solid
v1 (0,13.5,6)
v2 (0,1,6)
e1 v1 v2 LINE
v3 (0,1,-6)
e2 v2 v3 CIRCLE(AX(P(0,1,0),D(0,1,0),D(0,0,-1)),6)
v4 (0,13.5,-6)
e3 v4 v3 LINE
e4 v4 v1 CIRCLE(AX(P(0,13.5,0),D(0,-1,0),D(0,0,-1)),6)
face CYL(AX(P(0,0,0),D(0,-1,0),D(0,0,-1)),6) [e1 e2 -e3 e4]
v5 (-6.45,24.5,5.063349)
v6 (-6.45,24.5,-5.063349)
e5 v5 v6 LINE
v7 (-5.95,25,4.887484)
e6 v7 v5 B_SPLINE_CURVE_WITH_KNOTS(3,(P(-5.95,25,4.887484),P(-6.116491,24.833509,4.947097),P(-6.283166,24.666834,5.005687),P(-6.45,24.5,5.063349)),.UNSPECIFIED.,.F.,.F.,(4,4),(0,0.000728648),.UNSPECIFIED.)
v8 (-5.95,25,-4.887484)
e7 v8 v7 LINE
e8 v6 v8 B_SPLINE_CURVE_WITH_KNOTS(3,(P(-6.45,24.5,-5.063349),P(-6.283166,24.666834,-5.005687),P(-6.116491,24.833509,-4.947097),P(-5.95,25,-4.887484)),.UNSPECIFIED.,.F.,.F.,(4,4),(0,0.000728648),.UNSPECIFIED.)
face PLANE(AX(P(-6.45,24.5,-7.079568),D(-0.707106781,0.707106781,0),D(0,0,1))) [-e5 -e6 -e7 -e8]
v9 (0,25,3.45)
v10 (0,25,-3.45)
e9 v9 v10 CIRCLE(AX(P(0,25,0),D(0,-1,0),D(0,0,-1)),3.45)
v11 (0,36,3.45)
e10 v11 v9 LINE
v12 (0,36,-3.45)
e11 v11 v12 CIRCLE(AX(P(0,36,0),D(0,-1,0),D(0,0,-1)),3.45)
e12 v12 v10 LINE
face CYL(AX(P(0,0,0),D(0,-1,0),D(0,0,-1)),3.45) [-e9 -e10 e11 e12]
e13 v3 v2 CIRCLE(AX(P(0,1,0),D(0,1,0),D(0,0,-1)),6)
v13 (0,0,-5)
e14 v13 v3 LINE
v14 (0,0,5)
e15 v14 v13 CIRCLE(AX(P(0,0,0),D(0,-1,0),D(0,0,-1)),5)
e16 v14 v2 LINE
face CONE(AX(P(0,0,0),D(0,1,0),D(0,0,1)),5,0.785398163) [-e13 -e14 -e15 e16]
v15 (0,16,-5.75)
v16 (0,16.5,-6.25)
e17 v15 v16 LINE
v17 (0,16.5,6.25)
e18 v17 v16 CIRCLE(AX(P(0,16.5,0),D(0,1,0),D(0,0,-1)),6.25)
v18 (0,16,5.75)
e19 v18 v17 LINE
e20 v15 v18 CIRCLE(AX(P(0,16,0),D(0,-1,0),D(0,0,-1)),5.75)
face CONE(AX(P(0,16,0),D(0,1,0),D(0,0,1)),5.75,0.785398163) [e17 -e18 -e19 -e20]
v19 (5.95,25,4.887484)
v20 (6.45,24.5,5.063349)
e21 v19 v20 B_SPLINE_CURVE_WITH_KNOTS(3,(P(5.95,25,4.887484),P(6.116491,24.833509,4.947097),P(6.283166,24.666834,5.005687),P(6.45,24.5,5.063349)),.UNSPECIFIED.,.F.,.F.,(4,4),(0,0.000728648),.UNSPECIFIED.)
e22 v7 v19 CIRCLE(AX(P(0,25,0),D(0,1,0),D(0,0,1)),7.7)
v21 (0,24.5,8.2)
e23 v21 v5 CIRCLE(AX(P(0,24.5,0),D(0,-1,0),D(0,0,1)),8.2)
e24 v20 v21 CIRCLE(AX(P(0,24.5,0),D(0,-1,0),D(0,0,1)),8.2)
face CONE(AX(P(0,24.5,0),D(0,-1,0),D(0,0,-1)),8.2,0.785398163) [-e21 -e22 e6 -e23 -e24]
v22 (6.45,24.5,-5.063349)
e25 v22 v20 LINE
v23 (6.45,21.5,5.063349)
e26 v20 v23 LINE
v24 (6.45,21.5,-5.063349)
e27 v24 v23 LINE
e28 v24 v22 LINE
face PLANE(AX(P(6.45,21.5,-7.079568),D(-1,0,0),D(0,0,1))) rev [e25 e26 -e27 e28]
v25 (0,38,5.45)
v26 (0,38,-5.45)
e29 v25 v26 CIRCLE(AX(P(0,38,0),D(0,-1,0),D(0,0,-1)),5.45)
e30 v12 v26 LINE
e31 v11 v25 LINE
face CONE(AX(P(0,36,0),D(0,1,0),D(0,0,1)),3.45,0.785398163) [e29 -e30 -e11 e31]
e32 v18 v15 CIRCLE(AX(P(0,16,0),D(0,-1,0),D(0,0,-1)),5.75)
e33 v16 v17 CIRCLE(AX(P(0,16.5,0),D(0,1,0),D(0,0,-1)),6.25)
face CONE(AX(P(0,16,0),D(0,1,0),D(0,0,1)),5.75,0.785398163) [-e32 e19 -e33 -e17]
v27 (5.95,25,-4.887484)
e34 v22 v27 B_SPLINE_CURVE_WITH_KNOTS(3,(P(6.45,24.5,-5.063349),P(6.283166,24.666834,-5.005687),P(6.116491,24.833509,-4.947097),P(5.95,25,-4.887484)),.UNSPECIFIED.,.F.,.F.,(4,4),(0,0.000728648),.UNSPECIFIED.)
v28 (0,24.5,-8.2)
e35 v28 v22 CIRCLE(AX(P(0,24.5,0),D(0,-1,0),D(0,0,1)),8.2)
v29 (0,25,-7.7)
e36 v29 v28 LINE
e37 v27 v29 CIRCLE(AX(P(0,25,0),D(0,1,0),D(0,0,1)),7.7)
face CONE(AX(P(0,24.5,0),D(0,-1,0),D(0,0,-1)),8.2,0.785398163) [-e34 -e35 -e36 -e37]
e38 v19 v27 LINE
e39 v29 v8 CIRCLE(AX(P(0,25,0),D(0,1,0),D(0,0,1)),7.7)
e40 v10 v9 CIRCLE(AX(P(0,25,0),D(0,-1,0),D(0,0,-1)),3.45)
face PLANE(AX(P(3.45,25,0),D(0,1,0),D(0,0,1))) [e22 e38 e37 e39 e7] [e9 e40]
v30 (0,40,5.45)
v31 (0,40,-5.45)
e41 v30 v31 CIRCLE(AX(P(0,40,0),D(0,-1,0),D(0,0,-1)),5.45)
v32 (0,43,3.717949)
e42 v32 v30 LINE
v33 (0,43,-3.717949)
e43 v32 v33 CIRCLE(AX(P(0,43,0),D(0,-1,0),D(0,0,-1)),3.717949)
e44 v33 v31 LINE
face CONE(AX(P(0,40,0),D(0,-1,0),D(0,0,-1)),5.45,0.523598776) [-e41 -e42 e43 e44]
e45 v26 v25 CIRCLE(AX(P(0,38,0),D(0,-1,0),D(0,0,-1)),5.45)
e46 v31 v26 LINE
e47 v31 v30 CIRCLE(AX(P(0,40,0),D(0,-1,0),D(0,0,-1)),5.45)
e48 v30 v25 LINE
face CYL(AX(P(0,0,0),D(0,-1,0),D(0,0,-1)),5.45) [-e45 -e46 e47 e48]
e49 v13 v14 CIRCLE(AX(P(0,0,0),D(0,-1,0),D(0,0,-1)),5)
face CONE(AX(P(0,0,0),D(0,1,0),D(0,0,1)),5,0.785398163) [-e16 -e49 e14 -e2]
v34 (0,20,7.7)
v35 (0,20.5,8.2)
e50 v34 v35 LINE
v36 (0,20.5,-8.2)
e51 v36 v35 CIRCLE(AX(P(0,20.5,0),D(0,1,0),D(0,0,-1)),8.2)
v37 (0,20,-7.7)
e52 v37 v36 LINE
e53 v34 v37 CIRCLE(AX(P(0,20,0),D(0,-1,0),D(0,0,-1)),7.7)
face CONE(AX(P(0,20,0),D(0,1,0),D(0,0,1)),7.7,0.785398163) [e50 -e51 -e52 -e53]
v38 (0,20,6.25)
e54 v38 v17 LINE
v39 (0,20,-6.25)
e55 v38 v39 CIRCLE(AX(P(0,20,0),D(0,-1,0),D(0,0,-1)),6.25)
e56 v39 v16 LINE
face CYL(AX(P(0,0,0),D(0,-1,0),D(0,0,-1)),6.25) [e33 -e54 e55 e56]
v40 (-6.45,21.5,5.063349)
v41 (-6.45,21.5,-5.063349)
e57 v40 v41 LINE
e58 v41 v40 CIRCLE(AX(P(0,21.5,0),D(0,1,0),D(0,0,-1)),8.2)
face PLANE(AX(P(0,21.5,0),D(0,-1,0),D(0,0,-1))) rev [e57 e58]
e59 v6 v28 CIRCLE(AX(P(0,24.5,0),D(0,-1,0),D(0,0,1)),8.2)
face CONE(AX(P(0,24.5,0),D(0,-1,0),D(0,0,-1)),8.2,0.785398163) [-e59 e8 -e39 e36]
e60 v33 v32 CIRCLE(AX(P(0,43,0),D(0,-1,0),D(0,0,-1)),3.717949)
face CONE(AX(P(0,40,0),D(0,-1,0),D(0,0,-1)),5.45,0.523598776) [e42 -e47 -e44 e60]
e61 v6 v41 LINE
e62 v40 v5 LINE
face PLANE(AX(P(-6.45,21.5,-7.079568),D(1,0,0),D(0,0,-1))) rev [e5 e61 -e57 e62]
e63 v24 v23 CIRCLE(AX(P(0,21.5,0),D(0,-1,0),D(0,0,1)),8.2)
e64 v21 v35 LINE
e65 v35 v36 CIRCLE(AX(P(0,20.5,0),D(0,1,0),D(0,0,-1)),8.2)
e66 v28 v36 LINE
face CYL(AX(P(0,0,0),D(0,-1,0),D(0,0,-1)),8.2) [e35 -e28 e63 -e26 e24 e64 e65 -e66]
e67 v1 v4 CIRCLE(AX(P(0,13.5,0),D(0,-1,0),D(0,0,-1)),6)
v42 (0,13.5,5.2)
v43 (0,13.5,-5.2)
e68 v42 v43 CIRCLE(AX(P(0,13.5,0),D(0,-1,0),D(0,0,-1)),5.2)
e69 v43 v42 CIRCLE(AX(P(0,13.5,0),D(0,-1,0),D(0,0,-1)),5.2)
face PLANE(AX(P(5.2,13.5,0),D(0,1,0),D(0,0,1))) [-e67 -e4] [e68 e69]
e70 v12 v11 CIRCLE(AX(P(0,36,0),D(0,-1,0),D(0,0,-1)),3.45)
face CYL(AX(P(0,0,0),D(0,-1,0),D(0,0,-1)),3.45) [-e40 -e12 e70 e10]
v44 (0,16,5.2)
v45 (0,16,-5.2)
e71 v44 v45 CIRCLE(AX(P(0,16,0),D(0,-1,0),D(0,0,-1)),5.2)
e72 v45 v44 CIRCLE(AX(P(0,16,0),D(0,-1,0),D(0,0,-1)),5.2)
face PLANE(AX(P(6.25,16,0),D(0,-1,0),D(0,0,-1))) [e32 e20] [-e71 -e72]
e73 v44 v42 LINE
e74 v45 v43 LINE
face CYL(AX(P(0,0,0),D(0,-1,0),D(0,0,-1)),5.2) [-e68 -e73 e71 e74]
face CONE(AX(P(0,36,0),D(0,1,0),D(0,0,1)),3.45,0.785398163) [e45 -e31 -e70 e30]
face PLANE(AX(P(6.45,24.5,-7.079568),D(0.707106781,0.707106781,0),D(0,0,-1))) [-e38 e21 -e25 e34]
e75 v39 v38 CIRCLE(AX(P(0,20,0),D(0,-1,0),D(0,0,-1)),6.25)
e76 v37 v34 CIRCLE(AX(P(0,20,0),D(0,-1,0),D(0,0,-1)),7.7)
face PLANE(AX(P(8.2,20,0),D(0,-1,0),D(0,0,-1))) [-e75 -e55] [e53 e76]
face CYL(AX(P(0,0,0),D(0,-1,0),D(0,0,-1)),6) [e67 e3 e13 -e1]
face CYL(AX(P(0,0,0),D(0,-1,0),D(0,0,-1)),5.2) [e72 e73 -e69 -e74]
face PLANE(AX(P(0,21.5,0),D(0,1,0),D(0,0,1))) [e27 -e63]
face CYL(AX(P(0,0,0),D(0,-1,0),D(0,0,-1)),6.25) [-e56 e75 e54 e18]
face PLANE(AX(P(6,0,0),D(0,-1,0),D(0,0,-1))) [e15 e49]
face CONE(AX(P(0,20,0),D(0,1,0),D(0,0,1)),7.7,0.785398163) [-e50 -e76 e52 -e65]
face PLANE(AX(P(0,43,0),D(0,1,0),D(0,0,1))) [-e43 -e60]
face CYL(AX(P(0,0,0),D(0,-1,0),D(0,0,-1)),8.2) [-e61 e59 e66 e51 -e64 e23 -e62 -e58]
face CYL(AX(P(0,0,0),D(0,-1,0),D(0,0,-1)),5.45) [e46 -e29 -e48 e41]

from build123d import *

# Parameters (mm, degrees)
CHAMFER_1_SIZE      = 1
SKETCH_2_W          = 3.929205492
SKETCH_2_H          = 14.159135618
CUT_EXTRUDE_1_DEPTH = 3.5
CHAMFER_2_SIZE      = 0.5


with BuildPart() as part:
    # 草图1 → 旋转1 (revolve)
    with BuildSketch(Plane.XY, mode=Mode.PRIVATE) as revolve_1_sk:
        Polygon((0, 43), (3.717949192, 43), (5.45, 40), (5.45, 38), (3.45, 36), (3.45, 25), (8.2, 25), (8.2, 20), (6.25, 20), (6.25, 16), (5.2, 16), (5.2, 13.5), (6, 13.5), (6, 0), (0, 0), align=None)
    revolve(revolve_1_sk.sketch.rotate(Axis((0, 0, 0), (0, 1, 0)), 90), axis=Axis((0, 0, 0), (0, 1, 0)))

    # 倒角1
    chamfer_1_edges = [part.edges().sort_by_distance(p)[0] for p in [
        (0, 0, 6),
    ]]
    chamfer(chamfer_1_edges, length=CHAMFER_1_SIZE)

    # 草图2 → 切除-拉伸1 (cut)
    with BuildSketch(Plane(origin=(0, 25, 0), x_dir=(1, 0, 0), z_dir=(0, 1, 0))):
        with Locations((-8.414602746, 0)):
            Rectangle(SKETCH_2_W, SKETCH_2_H)
        with Locations((8.414602746, 0)):
            Rectangle(SKETCH_2_W, SKETCH_2_H)
    extrude(amount=-CUT_EXTRUDE_1_DEPTH, mode=Mode.SUBTRACT)

    # 倒角2
    chamfer_2_edges = [part.edges().sort_by_distance(p)[0] for p in [
        (0, 16, 6.25),
        (0, 20, 8.2),
        (0, 25, 8.2),
        (3.58612191, 25, -7.374261295),
        (-6.45, 25, 0),
        (6.45, 25, 0),
    ]]
    chamfer(chamfer_2_edges, length=CHAMFER_2_SIZE)


solid = part.part
